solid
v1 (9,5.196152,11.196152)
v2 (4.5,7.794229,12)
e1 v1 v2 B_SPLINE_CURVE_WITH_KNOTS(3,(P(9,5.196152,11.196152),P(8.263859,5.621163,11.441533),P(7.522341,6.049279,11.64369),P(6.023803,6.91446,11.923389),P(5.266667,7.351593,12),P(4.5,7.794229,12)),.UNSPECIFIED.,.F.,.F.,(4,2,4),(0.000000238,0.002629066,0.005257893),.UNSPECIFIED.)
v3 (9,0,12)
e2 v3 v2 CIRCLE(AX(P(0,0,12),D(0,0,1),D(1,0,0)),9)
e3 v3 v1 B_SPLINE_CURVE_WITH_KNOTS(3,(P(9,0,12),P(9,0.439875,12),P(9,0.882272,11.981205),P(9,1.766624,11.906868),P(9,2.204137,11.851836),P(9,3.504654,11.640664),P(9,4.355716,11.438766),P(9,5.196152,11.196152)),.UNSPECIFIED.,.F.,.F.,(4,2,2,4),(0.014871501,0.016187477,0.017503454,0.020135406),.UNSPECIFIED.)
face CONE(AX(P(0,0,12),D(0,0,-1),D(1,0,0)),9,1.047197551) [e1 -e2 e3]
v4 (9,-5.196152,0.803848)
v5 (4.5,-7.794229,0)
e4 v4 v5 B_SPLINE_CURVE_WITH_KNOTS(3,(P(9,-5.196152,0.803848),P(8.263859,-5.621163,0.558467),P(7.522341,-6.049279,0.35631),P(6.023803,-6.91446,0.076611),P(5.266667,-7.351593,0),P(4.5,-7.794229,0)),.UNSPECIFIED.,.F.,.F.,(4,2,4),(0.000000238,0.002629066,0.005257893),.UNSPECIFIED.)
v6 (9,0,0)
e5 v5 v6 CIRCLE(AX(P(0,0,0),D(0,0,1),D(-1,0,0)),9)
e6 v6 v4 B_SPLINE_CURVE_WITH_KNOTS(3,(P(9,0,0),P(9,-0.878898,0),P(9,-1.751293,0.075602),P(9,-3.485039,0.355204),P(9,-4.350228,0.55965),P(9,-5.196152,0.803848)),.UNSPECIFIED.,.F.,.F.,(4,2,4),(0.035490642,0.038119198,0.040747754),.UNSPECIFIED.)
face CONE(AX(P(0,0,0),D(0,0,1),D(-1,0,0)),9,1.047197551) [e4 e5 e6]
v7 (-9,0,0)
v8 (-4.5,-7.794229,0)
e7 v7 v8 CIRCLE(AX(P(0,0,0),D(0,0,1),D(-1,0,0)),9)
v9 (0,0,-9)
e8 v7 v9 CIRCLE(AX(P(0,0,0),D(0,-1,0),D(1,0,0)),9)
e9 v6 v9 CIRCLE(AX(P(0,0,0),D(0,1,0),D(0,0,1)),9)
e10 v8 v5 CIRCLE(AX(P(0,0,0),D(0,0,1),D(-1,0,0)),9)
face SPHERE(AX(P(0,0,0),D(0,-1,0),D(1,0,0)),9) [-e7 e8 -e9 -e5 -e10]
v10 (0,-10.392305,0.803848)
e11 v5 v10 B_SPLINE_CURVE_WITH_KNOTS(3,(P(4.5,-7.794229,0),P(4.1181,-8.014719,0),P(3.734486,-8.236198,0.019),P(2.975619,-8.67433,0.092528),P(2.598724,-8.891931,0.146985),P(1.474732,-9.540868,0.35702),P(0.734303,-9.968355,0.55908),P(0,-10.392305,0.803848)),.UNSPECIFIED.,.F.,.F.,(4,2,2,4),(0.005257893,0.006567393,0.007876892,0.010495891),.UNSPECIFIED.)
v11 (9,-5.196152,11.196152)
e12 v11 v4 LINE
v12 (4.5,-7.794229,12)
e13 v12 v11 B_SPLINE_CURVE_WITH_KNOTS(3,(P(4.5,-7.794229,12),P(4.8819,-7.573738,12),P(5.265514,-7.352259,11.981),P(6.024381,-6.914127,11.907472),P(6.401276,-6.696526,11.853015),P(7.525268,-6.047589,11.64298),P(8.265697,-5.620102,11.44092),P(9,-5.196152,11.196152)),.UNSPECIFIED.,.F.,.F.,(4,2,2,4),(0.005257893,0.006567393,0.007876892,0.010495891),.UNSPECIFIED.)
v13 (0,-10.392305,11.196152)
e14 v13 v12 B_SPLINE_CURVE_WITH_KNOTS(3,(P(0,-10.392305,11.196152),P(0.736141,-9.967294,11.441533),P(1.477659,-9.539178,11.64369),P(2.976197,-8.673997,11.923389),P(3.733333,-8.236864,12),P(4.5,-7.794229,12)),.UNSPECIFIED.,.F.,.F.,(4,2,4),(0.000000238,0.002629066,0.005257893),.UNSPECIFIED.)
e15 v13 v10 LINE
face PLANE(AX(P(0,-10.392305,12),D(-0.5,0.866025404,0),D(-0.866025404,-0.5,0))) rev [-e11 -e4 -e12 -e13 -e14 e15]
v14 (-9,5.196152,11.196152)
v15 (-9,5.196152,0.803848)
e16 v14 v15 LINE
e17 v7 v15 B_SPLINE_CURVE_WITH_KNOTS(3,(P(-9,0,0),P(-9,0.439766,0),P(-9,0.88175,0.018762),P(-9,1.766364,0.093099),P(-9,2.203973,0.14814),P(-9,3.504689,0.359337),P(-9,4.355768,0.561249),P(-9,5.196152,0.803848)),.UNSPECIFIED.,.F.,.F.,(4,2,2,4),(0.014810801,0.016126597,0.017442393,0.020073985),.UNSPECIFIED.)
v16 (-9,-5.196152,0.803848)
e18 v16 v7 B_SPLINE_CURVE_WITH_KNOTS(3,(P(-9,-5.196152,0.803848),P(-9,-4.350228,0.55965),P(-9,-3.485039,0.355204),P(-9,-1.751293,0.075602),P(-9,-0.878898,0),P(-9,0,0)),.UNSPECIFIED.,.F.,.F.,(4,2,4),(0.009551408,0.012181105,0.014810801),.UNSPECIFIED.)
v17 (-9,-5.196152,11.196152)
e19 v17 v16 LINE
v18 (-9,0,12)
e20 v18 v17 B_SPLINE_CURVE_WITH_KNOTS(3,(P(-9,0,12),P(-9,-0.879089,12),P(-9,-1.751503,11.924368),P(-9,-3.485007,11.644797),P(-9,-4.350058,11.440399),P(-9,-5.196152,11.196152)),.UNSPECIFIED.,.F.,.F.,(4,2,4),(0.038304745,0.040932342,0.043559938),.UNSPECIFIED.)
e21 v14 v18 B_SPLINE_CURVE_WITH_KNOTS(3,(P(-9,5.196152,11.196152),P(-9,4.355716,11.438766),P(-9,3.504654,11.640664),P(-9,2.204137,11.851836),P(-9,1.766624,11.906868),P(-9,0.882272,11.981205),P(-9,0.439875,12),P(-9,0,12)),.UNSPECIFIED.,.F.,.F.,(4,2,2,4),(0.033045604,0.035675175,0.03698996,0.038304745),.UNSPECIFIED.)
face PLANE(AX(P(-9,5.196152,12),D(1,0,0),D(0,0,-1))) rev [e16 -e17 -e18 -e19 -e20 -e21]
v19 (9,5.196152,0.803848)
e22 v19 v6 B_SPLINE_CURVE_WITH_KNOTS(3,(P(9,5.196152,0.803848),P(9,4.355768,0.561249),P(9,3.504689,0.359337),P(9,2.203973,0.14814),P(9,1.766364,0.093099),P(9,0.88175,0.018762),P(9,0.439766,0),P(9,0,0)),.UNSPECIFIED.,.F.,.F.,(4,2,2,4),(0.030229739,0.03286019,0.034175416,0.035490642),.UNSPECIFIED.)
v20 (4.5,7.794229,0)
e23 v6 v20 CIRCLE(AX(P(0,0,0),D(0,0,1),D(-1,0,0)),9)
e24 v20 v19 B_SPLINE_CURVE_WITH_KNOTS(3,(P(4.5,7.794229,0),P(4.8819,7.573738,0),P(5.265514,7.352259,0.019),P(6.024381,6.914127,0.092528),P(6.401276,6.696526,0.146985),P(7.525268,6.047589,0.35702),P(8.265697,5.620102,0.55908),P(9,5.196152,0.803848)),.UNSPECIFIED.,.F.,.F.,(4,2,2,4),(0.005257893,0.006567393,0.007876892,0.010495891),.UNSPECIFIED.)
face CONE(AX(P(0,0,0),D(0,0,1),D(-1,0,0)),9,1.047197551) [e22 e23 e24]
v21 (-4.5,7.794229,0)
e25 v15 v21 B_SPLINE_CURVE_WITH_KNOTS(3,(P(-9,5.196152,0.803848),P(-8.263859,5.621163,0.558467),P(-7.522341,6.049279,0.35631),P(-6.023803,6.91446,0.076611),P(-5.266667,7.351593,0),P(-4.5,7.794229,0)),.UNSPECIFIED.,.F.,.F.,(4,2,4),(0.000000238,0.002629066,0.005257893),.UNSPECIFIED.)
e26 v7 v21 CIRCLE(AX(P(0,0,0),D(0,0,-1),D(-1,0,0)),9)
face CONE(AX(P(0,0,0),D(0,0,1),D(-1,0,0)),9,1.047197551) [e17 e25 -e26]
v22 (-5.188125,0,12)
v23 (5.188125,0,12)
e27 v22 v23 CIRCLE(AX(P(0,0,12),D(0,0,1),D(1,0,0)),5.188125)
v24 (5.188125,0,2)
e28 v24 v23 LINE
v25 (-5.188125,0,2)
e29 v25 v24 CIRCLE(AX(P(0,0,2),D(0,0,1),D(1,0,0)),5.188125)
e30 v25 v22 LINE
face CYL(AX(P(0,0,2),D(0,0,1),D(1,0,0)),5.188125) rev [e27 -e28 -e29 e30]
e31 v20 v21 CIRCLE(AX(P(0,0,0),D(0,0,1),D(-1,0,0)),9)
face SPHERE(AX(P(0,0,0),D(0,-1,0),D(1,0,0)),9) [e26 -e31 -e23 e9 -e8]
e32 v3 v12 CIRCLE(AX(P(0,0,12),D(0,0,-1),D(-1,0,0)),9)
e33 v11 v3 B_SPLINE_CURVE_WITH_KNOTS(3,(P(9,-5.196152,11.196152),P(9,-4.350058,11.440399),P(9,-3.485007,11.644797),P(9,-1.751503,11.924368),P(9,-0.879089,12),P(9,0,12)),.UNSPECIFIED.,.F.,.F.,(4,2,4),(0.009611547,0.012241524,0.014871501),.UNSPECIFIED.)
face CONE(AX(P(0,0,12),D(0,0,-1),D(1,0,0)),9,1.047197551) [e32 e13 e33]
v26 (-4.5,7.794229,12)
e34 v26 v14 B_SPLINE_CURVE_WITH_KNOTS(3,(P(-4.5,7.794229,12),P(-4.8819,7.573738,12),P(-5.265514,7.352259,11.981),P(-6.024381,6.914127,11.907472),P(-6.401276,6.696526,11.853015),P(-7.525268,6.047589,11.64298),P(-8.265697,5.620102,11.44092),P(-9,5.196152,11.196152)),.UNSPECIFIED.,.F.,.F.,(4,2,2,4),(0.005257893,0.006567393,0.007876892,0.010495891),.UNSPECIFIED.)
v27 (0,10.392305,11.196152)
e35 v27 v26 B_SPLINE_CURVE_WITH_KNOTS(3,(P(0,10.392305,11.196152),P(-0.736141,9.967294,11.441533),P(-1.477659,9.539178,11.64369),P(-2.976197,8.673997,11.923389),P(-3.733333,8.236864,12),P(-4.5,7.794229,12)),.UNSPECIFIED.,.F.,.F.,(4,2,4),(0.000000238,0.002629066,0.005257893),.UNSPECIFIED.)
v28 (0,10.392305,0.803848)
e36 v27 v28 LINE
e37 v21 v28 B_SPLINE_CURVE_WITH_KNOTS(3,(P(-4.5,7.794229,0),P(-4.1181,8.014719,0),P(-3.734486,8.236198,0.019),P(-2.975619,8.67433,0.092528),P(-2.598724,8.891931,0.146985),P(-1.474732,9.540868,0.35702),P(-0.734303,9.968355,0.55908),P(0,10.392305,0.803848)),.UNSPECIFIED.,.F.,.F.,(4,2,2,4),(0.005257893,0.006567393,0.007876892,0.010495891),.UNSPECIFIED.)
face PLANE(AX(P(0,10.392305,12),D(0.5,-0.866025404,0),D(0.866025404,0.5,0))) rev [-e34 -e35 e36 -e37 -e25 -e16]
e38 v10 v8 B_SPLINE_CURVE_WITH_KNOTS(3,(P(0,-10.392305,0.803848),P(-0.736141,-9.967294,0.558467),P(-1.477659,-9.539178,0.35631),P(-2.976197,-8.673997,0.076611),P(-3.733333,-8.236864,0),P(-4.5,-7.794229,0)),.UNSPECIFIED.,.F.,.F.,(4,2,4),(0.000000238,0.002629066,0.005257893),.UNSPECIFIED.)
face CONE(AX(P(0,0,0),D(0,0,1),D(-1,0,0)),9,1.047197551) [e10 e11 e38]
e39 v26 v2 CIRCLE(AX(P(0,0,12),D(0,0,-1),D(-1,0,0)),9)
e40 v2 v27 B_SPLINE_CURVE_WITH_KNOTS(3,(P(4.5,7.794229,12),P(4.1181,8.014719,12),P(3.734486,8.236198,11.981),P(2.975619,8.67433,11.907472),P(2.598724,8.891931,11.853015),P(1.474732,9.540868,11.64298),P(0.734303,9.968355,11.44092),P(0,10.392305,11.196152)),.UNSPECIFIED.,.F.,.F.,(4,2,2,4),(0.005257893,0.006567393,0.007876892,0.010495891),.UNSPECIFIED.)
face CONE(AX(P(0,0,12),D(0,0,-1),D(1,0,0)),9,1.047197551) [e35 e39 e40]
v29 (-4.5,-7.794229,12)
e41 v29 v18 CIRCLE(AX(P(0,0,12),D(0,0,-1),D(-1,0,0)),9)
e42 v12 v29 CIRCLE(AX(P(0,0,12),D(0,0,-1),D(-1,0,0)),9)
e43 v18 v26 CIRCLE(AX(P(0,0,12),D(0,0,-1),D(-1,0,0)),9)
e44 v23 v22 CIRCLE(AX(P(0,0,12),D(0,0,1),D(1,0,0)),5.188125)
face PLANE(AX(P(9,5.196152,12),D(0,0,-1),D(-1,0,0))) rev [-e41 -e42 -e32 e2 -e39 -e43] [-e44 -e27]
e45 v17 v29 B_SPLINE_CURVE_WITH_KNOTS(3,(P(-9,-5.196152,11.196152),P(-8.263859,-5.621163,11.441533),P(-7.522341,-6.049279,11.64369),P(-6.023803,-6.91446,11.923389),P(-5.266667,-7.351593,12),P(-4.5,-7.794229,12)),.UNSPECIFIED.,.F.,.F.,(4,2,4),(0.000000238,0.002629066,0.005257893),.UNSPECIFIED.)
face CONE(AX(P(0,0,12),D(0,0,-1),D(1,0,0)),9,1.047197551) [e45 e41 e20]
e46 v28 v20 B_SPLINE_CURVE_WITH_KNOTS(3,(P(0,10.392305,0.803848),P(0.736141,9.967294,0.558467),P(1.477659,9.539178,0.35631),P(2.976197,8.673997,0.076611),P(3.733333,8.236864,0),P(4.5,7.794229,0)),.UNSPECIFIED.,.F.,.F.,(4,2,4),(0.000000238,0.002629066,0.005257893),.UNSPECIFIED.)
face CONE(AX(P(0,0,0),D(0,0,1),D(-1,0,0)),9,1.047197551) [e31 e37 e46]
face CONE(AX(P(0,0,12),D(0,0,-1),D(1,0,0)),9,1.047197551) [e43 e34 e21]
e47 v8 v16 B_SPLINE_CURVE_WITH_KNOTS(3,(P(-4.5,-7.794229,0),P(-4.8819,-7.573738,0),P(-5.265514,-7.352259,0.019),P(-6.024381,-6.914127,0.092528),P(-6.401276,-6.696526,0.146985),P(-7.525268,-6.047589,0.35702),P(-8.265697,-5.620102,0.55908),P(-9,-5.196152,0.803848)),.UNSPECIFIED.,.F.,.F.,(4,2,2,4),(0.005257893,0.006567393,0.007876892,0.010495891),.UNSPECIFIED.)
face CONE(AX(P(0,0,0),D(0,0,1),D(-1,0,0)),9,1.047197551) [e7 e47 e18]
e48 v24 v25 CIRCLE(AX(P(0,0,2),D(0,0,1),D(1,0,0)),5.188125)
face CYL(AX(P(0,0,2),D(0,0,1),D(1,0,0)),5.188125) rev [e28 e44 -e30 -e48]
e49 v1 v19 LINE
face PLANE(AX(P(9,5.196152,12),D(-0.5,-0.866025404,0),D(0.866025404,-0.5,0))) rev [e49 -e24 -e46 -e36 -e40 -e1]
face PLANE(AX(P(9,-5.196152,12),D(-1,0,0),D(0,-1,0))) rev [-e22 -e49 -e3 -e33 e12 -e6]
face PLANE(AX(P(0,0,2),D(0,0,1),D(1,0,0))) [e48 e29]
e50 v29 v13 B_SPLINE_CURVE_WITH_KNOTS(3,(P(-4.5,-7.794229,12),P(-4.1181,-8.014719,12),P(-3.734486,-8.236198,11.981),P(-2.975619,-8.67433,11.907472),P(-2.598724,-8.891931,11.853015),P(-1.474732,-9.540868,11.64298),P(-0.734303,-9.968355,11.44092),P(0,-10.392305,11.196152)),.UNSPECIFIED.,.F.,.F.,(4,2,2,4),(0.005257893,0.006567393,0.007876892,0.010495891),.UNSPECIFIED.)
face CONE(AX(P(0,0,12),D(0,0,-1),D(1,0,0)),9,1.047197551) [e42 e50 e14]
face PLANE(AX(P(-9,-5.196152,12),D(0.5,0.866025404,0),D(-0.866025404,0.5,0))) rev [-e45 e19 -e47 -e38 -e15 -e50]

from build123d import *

# Parameters (mm, degrees)
EXTRUDE_575_DEPTH   = 12
SKETCH_4_OUTSIDE_W  = 93.598
SKETCH_4_OUTSIDE_H  = 96.382
SKETCH_4_OUTSIDE_R  = 9
CUT_EXTRUDE_1_DEPTH = 19.248287591
CUT_EXTRUDE_1_DRAFT = -60
SKETCH_5_OUTSIDE_W  = 117.332
SKETCH_5_OUTSIDE_H  = 120.116
SKETCH_5_OUTSIDE_R  = 9
CUT_EXTRUDE_2_DEPTH = 26.099800796
CUT_EXTRUDE_2_DRAFT = -60
SKETCH_6_R          = 5.188125
CUT_EXTRUDE_3_DEPTH = 10


with BuildPart() as part:
    # 草图1 → Extrude 575 (new body)
    with BuildSketch(Plane.XY):
        Polygon((0, 10.392304845), (-9, 5.196152423), (-9, -5.196152423), (0, -10.392304845), (9, -5.196152423), (9, 5.196152423), align=None)
    extrude(amount=EXTRUDE_575_DEPTH)

    # 草图2 → 凸台-旋转1 (revolve)
    with BuildSketch(Plane(origin=(0, 0, 0), x_dir=(1, 0, 0), z_dir=(0, 1, 0))):
        with BuildLine():
            Line((0, 9), (0, 0))
            Line((0, 0), (9, 0))
            ThreePointArc((9, 0), (6.363961031, 6.363961031), (0, 9))
        make_face()
    revolve(axis=Axis((0, 0, -2.579649935), (0, 0, 1)))


with BuildPart() as cut_extrude_1_tool:
    # 草图4 outside → 切除-拉伸1 (with draft: the straight prism first)
    with BuildSketch(Plane(origin=(0, 0, 0), x_dir=(-1, 0, 0), z_dir=(0, 0, -1))):
        Rectangle(SKETCH_4_OUTSIDE_W, SKETCH_4_OUTSIDE_H)
        Circle(SKETCH_4_OUTSIDE_R, mode=Mode.SUBTRACT)
    extrude(amount=-CUT_EXTRUDE_1_DEPTH)
    # 切除-拉伸1: the draft: its side faces are tilted about the plane it starts from
    cut_extrude_1_sides = [cut_extrude_1_tool.faces().sort_by_distance(p)[0] for p in [
        (0, -48.191, 9.624143795),
        (-46.799, 0, 9.624143795),
        (0, 48.191, 9.624143795),
        (46.799, 0, 9.624143795),
        (9, 0, 9.624143795),
    ]]
    draft(cut_extrude_1_sides, Plane(origin=(0, 0, 0), x_dir=(-1, 0, 0), z_dir=(0, 0, -1)), CUT_EXTRUDE_1_DRAFT)


with BuildPart() as part_1:
    add(part.part)

    # 切除-拉伸1: cut by cut_extrude_1_tool
    add(cut_extrude_1_tool.part, mode=Mode.SUBTRACT)


with BuildPart() as cut_extrude_2_tool:
    # 草图5 outside → 切除-拉伸2 (with draft: the straight prism first)
    with BuildSketch(Plane.XY.offset(12)):
        Rectangle(SKETCH_5_OUTSIDE_W, SKETCH_5_OUTSIDE_H)
        Circle(SKETCH_5_OUTSIDE_R, mode=Mode.SUBTRACT)
    extrude(amount=-CUT_EXTRUDE_2_DEPTH)
    # 切除-拉伸2: the draft: its side faces are tilted about the plane it starts from
    cut_extrude_2_sides = [cut_extrude_2_tool.faces().sort_by_distance(p)[0] for p in [
        (0, -60.058, -1.049900398),
        (58.666, 0, -1.049900398),
        (0, 60.058, -1.049900398),
        (-58.666, 0, -1.049900398),
        (-9, 0, -1.049900398),
    ]]
    draft(cut_extrude_2_sides, Plane.XY.offset(12), CUT_EXTRUDE_2_DRAFT)


with BuildPart() as part_2:
    add(part_1.part)

    # 切除-拉伸2: cut by cut_extrude_2_tool
    add(cut_extrude_2_tool.part, mode=Mode.SUBTRACT)

    # 草图6 → 切除-拉伸3 (cut)
    with BuildSketch(Plane.XY.offset(12)):
        Circle(SKETCH_6_R)
    extrude(amount=-CUT_EXTRUDE_3_DEPTH, mode=Mode.SUBTRACT)


solid = part_2.part
